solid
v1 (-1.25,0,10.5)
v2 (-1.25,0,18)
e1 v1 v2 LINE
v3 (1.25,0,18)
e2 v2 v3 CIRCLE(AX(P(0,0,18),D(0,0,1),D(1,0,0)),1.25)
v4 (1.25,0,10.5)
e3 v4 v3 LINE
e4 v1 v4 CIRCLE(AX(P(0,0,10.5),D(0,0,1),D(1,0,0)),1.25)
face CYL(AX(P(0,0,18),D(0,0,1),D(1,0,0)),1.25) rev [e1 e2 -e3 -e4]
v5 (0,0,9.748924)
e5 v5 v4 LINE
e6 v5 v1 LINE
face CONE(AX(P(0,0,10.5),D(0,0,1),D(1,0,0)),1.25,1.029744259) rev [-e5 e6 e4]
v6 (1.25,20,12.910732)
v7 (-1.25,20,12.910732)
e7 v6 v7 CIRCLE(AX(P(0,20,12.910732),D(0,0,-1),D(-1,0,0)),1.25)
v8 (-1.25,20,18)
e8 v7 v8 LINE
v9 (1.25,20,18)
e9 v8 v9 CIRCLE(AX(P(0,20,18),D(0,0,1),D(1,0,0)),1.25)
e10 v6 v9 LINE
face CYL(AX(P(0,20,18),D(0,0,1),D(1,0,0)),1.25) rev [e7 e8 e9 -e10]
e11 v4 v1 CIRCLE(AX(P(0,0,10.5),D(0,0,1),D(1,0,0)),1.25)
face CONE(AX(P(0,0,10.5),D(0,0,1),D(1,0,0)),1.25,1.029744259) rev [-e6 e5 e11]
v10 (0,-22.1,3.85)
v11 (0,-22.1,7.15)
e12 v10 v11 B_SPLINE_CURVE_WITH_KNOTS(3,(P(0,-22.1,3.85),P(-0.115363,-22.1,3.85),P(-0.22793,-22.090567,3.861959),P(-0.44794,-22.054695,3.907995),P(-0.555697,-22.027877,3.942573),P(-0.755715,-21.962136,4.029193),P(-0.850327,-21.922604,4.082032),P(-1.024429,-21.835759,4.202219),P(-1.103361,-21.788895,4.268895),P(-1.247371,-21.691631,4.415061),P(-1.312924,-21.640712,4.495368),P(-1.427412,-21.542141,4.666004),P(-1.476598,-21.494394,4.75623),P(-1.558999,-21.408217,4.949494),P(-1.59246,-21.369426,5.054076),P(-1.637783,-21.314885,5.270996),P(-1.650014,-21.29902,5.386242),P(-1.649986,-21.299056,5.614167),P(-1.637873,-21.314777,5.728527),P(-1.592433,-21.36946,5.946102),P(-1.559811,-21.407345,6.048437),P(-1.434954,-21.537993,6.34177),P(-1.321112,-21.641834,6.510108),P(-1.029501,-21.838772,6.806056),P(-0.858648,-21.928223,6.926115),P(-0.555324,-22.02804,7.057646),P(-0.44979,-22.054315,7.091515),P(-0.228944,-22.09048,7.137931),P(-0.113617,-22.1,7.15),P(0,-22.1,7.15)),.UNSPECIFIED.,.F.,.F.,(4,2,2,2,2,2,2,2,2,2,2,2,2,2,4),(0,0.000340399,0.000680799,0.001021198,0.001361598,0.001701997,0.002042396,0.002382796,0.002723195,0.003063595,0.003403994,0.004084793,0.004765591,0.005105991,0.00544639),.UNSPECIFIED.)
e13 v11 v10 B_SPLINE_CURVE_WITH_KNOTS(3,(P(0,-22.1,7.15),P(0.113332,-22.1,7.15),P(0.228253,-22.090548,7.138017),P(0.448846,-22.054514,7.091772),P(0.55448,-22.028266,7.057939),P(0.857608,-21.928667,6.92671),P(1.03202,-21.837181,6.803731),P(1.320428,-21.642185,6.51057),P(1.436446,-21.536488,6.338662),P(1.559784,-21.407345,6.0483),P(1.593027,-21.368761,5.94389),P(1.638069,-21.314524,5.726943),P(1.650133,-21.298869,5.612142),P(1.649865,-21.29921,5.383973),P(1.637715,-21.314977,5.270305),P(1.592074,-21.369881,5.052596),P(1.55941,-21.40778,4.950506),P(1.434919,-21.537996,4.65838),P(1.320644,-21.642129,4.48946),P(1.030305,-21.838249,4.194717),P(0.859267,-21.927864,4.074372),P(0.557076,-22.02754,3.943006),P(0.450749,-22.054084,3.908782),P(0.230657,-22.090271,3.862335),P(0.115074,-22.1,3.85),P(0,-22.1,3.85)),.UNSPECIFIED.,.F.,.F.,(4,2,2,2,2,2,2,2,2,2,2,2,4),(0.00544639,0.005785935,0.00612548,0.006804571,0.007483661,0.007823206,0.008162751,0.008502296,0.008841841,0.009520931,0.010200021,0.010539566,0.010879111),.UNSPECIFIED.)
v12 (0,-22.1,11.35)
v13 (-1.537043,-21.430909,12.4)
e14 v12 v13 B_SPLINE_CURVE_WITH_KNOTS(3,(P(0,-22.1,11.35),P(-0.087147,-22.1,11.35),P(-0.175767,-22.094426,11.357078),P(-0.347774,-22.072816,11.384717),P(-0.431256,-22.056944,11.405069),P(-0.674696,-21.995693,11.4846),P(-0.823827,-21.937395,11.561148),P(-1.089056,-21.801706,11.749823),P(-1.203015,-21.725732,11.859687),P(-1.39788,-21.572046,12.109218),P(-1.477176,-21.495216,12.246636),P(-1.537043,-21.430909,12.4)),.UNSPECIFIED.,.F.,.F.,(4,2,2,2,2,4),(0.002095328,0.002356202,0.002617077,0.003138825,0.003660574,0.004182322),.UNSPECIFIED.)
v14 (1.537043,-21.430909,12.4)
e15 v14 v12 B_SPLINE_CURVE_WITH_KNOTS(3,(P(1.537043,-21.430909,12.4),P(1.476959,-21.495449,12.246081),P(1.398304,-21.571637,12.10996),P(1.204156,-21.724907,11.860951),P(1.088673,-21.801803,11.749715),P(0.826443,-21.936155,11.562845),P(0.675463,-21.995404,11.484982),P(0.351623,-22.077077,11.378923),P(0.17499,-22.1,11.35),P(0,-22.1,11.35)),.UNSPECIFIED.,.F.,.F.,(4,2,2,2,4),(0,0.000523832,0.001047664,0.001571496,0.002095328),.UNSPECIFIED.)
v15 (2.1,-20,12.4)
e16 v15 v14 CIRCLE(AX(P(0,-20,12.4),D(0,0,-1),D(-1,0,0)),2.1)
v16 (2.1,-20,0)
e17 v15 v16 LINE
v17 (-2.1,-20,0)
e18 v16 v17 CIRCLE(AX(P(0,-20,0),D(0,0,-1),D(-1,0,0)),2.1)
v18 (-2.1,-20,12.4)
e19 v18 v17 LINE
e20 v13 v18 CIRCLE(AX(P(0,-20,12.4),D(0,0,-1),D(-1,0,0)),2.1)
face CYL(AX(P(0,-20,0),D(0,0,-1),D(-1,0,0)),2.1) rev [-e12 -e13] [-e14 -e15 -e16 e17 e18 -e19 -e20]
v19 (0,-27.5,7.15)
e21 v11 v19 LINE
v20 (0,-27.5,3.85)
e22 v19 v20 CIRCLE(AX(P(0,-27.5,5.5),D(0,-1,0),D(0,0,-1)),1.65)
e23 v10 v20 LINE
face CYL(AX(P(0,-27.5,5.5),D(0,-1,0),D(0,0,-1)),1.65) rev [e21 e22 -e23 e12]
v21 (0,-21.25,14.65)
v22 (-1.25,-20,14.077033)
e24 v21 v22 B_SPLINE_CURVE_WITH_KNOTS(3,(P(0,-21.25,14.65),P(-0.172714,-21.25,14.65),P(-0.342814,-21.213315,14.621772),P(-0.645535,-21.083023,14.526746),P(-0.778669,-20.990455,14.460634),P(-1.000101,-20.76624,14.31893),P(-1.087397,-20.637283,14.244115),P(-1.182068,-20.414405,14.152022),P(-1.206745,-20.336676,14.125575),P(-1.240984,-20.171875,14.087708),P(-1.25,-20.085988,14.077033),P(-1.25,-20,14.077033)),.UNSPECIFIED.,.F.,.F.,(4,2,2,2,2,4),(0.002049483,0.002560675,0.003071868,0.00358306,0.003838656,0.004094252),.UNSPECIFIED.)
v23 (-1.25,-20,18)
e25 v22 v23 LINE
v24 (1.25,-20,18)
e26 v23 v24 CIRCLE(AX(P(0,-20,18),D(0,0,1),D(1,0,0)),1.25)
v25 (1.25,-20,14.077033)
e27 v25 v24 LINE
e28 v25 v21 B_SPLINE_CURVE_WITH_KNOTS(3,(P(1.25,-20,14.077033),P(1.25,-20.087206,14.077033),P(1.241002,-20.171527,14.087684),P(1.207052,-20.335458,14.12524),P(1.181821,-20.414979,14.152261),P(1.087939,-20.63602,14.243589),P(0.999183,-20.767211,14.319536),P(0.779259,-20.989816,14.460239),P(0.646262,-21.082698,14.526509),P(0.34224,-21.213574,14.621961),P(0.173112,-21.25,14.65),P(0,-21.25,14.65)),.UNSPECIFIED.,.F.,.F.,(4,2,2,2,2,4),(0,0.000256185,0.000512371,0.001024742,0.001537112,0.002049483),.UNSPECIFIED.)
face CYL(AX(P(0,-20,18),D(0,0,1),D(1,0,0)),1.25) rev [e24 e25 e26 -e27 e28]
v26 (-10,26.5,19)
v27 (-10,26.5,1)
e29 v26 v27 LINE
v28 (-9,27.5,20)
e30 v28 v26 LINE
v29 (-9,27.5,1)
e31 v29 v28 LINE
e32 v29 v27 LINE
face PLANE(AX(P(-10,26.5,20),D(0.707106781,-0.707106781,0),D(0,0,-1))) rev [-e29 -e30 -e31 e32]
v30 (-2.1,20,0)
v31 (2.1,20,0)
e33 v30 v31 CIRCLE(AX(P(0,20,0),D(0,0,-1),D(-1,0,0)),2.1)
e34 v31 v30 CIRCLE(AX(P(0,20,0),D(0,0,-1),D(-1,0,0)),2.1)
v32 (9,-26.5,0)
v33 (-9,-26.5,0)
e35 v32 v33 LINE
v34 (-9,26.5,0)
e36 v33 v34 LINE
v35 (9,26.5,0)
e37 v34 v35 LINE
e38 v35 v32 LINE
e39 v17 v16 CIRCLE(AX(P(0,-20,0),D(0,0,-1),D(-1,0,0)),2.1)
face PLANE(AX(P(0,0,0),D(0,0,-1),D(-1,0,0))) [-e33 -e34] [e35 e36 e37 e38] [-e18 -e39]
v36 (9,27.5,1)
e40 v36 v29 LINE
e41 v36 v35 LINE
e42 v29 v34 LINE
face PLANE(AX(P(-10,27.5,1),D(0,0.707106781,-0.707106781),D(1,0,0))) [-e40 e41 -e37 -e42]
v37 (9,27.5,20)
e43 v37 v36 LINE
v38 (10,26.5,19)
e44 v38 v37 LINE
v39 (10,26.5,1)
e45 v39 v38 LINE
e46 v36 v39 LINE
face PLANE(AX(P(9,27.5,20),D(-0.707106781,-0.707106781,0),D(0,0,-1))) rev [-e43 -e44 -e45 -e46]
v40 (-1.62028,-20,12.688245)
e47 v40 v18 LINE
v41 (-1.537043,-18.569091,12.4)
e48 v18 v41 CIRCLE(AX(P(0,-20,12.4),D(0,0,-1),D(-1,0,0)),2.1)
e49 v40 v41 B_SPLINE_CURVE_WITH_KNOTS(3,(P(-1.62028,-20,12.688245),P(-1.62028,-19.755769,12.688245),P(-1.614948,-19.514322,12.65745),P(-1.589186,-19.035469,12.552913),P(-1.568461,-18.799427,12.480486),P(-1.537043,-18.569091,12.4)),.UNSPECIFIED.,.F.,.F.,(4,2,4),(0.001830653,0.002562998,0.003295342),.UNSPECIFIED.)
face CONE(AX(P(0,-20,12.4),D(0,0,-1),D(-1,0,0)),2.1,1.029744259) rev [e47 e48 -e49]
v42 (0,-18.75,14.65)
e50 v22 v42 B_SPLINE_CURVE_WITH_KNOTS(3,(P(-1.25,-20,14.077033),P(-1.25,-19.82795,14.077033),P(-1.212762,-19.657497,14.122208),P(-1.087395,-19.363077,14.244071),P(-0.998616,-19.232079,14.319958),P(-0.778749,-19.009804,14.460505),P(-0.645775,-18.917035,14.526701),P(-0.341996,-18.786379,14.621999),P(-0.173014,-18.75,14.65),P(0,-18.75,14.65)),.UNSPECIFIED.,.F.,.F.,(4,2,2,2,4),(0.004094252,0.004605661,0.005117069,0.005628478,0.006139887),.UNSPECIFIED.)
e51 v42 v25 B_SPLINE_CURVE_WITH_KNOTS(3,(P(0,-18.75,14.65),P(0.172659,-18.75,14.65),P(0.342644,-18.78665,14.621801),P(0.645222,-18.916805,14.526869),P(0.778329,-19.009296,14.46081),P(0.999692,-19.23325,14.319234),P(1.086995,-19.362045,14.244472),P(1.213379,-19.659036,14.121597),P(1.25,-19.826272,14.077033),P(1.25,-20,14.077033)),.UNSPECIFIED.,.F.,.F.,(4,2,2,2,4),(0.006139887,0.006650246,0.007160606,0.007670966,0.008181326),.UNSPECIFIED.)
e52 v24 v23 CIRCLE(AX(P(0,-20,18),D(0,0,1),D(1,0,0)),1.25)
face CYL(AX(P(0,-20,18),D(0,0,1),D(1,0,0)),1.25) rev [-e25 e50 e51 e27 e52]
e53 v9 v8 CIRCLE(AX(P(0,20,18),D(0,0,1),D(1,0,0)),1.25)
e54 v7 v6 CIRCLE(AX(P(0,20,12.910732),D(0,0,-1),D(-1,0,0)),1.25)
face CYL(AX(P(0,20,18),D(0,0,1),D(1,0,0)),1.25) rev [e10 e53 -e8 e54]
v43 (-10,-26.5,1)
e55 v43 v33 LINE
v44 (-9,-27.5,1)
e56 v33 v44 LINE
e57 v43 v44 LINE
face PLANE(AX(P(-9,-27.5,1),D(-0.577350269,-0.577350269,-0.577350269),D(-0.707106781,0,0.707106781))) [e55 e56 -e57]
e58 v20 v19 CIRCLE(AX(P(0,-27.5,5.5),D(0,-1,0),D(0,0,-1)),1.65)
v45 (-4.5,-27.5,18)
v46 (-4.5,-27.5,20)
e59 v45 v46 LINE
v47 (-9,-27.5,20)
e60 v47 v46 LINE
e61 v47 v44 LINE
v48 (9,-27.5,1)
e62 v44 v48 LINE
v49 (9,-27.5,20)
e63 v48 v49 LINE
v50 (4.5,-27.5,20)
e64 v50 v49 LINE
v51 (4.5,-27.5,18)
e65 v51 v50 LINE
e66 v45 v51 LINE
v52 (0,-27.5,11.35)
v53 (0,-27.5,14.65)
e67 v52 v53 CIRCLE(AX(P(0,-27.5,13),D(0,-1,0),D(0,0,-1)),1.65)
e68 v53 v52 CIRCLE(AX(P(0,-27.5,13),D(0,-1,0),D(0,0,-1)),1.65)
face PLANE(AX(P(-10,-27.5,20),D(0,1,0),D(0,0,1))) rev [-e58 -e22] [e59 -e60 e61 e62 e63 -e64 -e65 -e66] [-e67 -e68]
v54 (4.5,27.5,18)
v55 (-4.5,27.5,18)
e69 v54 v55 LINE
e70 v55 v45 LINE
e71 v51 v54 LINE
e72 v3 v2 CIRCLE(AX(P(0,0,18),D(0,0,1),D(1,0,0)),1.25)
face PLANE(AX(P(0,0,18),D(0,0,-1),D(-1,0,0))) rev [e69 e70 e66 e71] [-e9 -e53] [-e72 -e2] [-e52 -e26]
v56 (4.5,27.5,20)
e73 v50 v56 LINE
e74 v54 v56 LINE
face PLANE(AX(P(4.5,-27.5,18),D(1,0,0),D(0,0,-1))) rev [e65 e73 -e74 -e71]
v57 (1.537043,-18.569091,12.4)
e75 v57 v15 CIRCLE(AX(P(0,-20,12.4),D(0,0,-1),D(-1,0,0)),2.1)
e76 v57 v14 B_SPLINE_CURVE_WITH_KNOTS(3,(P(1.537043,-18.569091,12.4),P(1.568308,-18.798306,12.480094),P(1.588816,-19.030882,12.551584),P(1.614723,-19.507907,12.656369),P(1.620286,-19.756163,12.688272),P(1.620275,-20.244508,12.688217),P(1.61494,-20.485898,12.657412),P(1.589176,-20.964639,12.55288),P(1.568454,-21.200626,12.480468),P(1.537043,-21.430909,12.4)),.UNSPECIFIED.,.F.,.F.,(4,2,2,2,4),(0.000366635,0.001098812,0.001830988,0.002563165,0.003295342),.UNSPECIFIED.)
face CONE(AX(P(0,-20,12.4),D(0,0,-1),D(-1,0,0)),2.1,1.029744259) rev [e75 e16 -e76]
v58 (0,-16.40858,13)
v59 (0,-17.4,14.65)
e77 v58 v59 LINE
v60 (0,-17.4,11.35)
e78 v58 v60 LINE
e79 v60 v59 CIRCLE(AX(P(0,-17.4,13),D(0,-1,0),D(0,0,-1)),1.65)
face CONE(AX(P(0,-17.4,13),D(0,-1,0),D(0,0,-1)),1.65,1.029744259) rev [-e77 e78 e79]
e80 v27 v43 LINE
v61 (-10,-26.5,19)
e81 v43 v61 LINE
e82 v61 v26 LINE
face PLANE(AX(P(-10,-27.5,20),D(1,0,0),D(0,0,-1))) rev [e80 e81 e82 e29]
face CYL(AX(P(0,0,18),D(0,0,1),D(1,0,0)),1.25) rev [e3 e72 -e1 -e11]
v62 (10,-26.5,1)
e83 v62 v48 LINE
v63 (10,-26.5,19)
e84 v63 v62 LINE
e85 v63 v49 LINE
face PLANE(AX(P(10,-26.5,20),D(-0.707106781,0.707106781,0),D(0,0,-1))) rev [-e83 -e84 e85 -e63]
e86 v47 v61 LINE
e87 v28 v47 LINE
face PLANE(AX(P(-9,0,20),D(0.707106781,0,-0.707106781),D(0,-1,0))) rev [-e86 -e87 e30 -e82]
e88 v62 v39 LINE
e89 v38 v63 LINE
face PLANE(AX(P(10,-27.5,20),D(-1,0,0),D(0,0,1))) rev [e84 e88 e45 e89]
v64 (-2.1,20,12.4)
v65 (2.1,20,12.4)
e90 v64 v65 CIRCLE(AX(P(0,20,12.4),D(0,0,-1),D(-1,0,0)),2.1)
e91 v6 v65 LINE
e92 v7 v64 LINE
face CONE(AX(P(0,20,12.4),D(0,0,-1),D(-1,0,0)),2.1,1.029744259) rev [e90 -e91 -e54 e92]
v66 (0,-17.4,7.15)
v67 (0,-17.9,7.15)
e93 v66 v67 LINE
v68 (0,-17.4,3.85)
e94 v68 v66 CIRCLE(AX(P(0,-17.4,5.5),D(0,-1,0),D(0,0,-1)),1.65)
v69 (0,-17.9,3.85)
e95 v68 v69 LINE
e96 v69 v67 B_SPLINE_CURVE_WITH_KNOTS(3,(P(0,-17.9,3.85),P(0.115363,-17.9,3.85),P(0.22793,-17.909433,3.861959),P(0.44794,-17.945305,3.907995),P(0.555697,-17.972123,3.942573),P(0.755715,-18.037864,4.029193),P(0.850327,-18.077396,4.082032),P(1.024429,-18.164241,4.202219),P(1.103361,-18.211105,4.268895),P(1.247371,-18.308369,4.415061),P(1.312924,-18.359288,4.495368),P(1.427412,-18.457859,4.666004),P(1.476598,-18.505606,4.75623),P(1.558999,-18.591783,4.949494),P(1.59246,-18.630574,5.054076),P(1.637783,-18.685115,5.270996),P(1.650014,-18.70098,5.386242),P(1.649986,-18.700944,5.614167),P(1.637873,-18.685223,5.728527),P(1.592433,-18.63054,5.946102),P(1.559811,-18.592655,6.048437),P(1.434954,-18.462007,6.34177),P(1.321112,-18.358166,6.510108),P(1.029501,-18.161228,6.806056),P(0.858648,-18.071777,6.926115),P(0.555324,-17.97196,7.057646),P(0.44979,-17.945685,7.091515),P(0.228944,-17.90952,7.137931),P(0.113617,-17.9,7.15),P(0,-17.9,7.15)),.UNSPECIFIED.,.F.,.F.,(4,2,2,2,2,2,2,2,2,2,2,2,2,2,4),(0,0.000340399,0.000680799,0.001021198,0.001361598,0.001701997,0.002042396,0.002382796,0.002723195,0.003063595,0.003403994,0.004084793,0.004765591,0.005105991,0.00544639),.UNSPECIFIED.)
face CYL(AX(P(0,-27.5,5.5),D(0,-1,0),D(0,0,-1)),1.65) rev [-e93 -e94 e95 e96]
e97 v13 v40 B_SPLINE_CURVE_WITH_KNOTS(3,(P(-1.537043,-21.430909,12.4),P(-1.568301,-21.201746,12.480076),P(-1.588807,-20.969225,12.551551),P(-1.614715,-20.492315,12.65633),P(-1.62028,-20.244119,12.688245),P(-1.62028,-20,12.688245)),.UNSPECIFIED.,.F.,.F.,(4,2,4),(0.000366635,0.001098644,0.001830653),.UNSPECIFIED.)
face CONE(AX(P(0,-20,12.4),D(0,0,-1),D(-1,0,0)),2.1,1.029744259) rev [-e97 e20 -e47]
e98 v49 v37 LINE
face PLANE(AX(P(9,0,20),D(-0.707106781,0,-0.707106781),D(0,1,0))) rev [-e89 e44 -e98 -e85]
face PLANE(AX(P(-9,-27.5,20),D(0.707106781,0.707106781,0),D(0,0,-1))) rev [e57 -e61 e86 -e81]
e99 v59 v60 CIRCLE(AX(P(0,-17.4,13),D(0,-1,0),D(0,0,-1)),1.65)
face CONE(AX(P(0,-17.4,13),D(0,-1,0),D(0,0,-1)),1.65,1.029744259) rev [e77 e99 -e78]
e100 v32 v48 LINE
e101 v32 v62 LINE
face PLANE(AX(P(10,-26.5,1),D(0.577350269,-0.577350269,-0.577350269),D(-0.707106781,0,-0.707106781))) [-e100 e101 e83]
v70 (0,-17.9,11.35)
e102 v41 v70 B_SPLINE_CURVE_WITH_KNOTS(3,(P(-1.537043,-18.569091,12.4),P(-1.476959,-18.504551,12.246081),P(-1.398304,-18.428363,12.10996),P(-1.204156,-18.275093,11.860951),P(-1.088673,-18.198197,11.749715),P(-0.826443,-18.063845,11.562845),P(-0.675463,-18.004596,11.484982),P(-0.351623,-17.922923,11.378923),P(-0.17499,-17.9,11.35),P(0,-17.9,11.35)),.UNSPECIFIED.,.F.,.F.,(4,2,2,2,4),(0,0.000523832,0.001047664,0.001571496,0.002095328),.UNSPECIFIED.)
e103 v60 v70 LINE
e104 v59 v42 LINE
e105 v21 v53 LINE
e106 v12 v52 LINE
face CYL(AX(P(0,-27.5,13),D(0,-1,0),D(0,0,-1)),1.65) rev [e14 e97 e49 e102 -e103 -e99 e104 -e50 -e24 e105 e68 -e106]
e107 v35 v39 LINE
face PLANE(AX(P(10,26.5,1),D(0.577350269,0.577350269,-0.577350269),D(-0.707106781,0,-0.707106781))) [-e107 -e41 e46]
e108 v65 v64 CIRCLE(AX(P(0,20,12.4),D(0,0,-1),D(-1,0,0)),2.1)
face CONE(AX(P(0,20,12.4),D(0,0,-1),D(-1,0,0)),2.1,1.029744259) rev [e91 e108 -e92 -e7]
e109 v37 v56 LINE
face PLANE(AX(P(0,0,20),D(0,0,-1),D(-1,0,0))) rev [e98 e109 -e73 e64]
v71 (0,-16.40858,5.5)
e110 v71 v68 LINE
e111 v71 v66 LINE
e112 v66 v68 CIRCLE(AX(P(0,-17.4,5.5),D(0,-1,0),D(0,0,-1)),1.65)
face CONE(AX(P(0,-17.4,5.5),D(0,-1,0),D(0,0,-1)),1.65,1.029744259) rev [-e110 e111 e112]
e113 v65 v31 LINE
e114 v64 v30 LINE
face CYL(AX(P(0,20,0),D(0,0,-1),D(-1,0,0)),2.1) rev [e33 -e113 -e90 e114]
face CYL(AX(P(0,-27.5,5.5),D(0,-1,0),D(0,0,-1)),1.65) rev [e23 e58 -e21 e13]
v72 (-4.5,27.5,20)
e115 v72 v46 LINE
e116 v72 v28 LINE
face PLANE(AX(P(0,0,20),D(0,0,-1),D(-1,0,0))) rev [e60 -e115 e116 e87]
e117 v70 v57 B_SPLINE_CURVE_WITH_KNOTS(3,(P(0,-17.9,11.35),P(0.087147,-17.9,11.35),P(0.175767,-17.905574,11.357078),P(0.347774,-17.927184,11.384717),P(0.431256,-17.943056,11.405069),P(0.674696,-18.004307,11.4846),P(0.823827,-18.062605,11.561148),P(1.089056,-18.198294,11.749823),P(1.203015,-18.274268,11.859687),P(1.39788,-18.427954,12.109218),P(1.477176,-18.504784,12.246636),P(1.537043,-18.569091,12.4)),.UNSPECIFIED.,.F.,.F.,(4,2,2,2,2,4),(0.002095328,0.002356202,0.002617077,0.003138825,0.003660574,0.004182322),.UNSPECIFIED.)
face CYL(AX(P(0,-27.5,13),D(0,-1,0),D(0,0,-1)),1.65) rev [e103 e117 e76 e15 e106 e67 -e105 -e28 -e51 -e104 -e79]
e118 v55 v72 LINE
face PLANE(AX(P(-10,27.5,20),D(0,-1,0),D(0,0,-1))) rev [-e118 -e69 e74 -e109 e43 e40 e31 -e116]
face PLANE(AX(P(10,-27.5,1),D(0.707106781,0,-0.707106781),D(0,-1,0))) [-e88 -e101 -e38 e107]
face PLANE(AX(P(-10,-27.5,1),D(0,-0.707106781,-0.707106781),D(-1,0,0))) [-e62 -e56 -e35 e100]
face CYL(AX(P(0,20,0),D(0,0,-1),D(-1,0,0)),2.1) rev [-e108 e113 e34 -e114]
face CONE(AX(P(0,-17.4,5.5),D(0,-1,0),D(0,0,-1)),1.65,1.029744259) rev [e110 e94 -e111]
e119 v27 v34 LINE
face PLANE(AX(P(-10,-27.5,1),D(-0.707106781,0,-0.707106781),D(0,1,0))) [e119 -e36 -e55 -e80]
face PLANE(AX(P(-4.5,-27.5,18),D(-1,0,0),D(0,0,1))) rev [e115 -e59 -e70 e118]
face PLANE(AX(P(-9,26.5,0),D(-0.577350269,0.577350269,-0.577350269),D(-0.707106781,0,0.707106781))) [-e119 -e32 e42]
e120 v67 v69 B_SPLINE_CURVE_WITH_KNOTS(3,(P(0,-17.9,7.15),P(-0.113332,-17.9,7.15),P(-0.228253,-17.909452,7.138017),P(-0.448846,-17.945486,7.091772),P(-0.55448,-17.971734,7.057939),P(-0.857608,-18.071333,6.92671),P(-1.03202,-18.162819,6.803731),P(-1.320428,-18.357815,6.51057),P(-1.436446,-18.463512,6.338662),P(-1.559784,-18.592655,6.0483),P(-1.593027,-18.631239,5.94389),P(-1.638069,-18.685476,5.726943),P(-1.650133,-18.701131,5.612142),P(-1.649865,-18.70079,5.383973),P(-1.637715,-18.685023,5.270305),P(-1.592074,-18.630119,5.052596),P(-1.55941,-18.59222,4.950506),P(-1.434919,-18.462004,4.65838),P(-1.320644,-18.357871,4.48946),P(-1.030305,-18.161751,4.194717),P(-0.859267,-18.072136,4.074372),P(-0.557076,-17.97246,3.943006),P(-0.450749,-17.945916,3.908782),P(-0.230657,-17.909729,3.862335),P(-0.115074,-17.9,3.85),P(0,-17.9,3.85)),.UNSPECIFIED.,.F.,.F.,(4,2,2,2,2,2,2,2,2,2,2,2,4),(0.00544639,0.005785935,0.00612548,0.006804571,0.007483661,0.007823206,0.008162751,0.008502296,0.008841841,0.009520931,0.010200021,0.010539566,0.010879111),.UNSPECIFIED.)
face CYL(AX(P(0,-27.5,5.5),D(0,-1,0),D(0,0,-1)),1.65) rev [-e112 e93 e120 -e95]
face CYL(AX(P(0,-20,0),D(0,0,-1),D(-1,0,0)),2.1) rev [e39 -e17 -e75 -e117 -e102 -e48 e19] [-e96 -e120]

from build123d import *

# Parameters (mm, degrees)
SKETCH1_W             = 20
SKETCH1_H             = 55
BOSS_EXTRUDE1_DEPTH   = 20
SKETCH2_W             = 9
SKETCH2_H             = 55
CUT_EXTRUDE1_DEPTH    = 2
M3_TAPPED_HOLE1_D     = 2.5
M3_TAPPED_HOLE1_DEPTH = 7.5
M3_TAPPED_HOLE1_TIP   = 0.751075774
M4_TAPPED_HOLE1_D     = 3.3
M4_TAPPED_HOLE1_DEPTH = 10.1
M4_TAPPED_HOLE1_TIP   = 0.991420021
M5_TAPPED_HOLE1_D     = 4.2
M5_TAPPED_HOLE1_DEPTH = 12.4
M5_TAPPED_HOLE1_TIP   = 1.2618073
CHAMFER1_SIZE         = 1


with BuildPart() as part:
    # Sketch1 → Boss-Extrude1 (new body)
    with BuildSketch(Plane.XY):
        Rectangle(SKETCH1_W, SKETCH1_H)
    extrude(amount=BOSS_EXTRUDE1_DEPTH)

    # Sketch2 → Cut-Extrude1 (cut)
    with BuildSketch(Plane.XY.offset(20)):
        Rectangle(SKETCH2_W, SKETCH2_H)
    extrude(amount=-CUT_EXTRUDE1_DEPTH, mode=Mode.SUBTRACT)

    # M3 Tapped Hole1
    with Locations(Plane.XY.offset(18)):
        with Locations((0, 20), (0, 0), (0, -20)):
            Hole(M3_TAPPED_HOLE1_D / 2, depth=M3_TAPPED_HOLE1_DEPTH)
            with Locations((0, 0, -(M3_TAPPED_HOLE1_DEPTH + M3_TAPPED_HOLE1_TIP / 2))):  # 118° drill point
                Cone(0, M3_TAPPED_HOLE1_D / 2, M3_TAPPED_HOLE1_TIP, mode=Mode.SUBTRACT)

    # M4 Tapped Hole1
    with Locations(Plane(origin=(0, -27.5, 0), x_dir=(-1, 0, 0), z_dir=(0, -1, 0))):
        with Locations((0, -13), (0, -5.5)):
            Hole(M4_TAPPED_HOLE1_D / 2, depth=M4_TAPPED_HOLE1_DEPTH)
            with Locations((0, 0, -(M4_TAPPED_HOLE1_DEPTH + M4_TAPPED_HOLE1_TIP / 2))):  # 118° drill point
                Cone(0, M4_TAPPED_HOLE1_D / 2, M4_TAPPED_HOLE1_TIP, mode=Mode.SUBTRACT)

    # M5 Tapped Hole1
    with Locations(Plane(origin=(0, 0, 0), x_dir=(-1, 0, 0), z_dir=(0, 0, -1))):
        with Locations((0, 20), (0, -20)):
            Hole(M5_TAPPED_HOLE1_D / 2, depth=M5_TAPPED_HOLE1_DEPTH)
            with Locations((0, 0, -(M5_TAPPED_HOLE1_DEPTH + M5_TAPPED_HOLE1_TIP / 2))):  # 118° drill point
                Cone(0, M5_TAPPED_HOLE1_D / 2, M5_TAPPED_HOLE1_TIP, mode=Mode.SUBTRACT)

    # Chamfer1
    chamfer1_edges = [part.edges().sort_by_distance(p)[0] for p in [
        (-10, 0, 20),
        (10, 0, 20),
        (0, -27.5, 0),
        (-10, 0, 0),
        (0, 27.5, 0),
        (10, 0, 0),
        (10, -27.5, 10),
        (-10, -27.5, 10),
        (-10, 27.5, 10),
        (10, 27.5, 10),
    ]]
    chamfer(chamfer1_edges, length=CHAMFER1_SIZE)


solid = part.part
